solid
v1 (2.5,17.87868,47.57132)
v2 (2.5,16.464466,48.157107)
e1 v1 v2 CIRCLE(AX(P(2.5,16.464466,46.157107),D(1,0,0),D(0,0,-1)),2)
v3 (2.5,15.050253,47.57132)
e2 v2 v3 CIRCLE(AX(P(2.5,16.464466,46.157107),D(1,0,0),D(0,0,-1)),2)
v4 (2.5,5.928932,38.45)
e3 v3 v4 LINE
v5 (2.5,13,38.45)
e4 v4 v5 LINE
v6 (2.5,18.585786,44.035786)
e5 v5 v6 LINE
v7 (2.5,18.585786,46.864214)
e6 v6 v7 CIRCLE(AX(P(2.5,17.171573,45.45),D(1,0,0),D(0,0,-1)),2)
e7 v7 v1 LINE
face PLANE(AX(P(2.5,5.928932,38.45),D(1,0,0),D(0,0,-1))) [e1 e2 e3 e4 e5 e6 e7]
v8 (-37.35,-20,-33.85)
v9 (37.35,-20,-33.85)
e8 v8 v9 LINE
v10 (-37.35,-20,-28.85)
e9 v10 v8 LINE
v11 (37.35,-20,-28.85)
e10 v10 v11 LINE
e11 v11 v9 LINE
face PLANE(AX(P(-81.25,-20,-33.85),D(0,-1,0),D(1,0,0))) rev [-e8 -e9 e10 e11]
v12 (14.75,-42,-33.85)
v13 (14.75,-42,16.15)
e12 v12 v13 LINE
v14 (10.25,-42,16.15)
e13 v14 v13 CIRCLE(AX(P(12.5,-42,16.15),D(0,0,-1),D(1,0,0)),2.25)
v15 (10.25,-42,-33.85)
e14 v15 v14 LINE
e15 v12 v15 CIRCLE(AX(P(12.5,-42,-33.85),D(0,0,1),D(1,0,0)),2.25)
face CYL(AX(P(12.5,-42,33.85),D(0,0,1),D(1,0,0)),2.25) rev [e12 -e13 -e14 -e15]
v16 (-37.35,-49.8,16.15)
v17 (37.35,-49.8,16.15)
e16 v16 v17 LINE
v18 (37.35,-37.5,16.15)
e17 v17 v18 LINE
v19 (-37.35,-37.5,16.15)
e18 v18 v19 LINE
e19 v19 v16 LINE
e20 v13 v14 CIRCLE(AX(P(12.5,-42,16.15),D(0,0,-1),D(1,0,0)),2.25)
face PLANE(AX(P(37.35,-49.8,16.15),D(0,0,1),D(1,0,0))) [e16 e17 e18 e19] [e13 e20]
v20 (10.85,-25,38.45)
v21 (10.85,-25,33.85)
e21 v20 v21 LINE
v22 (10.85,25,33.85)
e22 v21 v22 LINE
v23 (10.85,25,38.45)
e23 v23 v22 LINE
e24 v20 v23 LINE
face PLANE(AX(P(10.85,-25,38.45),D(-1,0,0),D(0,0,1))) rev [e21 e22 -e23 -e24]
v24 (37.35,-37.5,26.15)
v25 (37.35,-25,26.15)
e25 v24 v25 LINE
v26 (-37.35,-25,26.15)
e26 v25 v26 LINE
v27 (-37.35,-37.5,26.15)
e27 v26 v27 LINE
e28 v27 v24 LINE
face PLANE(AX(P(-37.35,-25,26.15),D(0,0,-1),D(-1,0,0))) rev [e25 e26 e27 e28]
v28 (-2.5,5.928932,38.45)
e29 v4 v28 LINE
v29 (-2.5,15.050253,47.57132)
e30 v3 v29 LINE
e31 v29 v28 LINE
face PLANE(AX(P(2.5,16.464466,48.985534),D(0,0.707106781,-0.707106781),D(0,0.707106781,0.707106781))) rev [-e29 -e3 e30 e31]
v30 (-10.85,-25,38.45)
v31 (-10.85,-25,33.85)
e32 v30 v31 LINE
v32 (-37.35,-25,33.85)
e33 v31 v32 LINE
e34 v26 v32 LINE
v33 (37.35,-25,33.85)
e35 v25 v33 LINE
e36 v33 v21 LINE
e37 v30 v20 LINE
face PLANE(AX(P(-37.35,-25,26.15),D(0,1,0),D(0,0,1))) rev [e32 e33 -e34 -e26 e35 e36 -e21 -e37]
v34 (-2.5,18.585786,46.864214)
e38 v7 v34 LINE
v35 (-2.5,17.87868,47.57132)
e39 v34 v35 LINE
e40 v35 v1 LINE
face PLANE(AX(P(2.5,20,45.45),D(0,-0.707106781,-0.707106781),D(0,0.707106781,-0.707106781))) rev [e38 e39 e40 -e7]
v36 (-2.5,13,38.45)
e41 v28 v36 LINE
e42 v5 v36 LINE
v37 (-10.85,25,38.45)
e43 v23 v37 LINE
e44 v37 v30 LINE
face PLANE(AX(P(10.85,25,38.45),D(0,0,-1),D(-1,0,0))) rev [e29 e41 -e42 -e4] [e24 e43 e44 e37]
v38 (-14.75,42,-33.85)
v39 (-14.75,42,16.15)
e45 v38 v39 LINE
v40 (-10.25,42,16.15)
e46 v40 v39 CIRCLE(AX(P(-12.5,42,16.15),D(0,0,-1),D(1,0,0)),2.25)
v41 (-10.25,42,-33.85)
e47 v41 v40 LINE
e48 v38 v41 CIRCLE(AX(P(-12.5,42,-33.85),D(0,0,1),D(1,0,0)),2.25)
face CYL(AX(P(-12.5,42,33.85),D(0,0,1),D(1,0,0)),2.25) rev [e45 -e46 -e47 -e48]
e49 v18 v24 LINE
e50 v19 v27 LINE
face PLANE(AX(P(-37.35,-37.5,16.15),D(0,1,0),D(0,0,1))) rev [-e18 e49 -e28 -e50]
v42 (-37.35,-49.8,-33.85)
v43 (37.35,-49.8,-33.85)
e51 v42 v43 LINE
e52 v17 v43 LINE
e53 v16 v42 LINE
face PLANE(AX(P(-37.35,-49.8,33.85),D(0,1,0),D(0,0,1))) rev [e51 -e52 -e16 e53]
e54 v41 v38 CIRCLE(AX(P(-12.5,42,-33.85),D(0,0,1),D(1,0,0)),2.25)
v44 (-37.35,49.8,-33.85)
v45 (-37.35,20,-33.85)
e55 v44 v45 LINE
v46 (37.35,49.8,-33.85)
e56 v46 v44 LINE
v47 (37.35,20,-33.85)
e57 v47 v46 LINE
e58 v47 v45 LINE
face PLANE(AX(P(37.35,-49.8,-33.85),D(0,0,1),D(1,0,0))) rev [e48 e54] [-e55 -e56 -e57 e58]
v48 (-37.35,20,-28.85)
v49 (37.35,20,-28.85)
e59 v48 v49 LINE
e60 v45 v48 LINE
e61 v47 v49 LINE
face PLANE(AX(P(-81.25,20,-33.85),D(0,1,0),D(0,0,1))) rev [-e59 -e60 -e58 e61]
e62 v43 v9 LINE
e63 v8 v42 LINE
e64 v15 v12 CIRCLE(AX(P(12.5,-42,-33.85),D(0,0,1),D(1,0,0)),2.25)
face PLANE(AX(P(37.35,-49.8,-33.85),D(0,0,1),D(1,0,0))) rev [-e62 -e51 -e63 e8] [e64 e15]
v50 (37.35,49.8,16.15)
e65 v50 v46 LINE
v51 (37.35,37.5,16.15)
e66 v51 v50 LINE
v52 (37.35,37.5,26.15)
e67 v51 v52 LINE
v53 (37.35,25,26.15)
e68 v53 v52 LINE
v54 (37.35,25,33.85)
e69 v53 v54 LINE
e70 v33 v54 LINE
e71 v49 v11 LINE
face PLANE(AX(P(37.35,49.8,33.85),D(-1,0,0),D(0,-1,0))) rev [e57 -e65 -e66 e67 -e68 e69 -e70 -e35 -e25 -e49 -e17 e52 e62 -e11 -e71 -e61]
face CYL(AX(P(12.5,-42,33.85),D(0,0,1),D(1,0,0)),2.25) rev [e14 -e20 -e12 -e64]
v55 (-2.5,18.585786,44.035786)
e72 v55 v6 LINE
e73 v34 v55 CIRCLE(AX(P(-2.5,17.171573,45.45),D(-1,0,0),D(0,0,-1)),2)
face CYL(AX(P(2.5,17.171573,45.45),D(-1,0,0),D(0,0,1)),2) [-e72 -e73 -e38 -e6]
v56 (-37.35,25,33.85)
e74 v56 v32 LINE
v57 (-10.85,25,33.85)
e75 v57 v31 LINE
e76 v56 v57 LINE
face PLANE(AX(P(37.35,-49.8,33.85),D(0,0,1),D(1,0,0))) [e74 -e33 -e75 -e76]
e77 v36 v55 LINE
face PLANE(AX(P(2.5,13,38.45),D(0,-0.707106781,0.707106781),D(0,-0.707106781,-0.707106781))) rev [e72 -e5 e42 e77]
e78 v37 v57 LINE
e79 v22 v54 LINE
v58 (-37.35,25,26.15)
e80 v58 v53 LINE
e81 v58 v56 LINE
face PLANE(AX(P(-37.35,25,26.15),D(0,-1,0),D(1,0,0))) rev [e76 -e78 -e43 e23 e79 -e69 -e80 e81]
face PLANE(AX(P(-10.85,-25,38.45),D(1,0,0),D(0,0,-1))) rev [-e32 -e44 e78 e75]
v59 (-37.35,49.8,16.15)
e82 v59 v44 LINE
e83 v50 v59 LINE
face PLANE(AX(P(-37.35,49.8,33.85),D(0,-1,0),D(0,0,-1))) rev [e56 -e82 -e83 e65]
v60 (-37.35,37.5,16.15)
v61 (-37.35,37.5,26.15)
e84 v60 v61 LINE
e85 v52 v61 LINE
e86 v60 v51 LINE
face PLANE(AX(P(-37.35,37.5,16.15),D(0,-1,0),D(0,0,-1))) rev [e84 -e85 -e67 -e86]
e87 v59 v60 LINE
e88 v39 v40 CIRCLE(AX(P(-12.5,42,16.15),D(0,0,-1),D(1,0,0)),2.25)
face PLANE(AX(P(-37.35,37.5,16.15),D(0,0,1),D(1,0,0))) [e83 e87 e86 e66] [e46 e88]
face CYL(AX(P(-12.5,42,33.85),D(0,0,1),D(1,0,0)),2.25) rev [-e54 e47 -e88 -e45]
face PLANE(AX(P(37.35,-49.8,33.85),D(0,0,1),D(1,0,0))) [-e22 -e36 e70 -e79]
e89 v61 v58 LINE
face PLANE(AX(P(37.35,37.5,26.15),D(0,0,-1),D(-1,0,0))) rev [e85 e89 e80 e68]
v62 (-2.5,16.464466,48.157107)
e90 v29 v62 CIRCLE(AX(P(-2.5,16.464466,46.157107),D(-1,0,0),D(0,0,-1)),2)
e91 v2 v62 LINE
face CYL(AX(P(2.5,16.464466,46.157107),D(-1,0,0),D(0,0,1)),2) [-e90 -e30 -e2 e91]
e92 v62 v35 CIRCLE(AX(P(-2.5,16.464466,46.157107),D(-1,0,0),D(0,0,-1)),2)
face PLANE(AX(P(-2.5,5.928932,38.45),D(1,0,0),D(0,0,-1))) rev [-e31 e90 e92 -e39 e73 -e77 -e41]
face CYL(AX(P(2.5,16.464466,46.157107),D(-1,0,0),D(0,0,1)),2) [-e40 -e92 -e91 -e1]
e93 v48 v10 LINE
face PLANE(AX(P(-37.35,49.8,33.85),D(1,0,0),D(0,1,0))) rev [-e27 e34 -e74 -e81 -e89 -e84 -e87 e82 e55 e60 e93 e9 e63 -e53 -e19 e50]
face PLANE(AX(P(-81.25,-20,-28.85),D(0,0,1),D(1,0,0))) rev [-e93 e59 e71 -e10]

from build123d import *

# Parameters (mm, degrees)
SKETCH1_W                  = 74.7
SKETCH1_H                  = 99.6
BOSS_EXTRUDE1_DEPTH        = 33.85
F_4_5_4_5_DIAMETER_HOLE1_D = 4.5
SKETCH4_W                  = 74.7
SKETCH4_H                  = 12.3
CUT_EXTRUDE1_DEPTH         = 17.7
SKETCH5_W                  = 74.7
SKETCH5_H                  = 12.5
CUT_EXTRUDE2_DEPTH         = 7.7
SKETCH6_W                  = 21.7
SKETCH6_H                  = 50
BOSS_EXTRUDE2_DEPTH        = 4.6
SKETCH7_W                  = 5
SKETCH7_H                  = 40
CUT_EXTRUDE3_DEPTH         = 118.6
BOSS_EXTRUDE3_DEPTH        = 2.5
FILLET1_R                  = 2


with BuildPart() as part:
    # Sketch1 → Boss-Extrude1 (new, symmetric)
    with BuildSketch(Plane.XY):
        Rectangle(SKETCH1_W, SKETCH1_H)
    extrude(amount=BOSS_EXTRUDE1_DEPTH, both=True)

    # Ø4.5 (4.5) Diameter Hole1 (through all)
    with Locations(Plane.XY.offset(33.85)):
        with Locations((-12.5, 42), (12.5, -42)):
            Hole(F_4_5_4_5_DIAMETER_HOLE1_D / 2)

    # Sketch4 → Cut-Extrude1 (cut)
    with BuildSketch(Plane.XY.offset(33.85)):
        with Locations((0, 43.65)):
            Rectangle(SKETCH4_W, SKETCH4_H)
        with Locations((0, -43.65)):
            Rectangle(SKETCH4_W, SKETCH4_H)
    extrude(amount=-CUT_EXTRUDE1_DEPTH, mode=Mode.SUBTRACT)

    # Sketch5 → Cut-Extrude2 (cut)
    with BuildSketch(Plane.XY.offset(33.85)):
        with Locations((0, -31.25)):
            Rectangle(SKETCH5_W, SKETCH5_H)
        with Locations((0, 31.25)):
            Rectangle(SKETCH5_W, SKETCH5_H)
    extrude(amount=-CUT_EXTRUDE2_DEPTH, mode=Mode.SUBTRACT)

    # Sketch6 → Boss-Extrude2 (add)
    with BuildSketch(Plane.XY.offset(33.85)):
        Rectangle(SKETCH6_W, SKETCH6_H)
    extrude(amount=BOSS_EXTRUDE2_DEPTH)

    # Sketch7 → Cut-Extrude3 (cut)
    with BuildSketch(Plane(origin=(37.35, 0, 0), x_dir=(0, 0, -1), z_dir=(1, 0, 0))):
        with Locations((31.35, 0)):
            Rectangle(SKETCH7_W, SKETCH7_H)
    extrude(amount=-CUT_EXTRUDE3_DEPTH, mode=Mode.SUBTRACT)

    # Sketch8 → Boss-Extrude3 (add, symmetric)
    with BuildSketch(Plane(origin=(0, 0, 0), x_dir=(0, 0, -1), z_dir=(1, 0, 0))):
        Polygon((-38.45, 13), (-45.45, 20), (-48.985533906, 16.464466094), (-38.45, 5.928932188), align=None)
    extrude(amount=BOSS_EXTRUDE3_DEPTH, both=True)

    # Fillet1
    fillet1_edges = [part.edges().sort_by_distance(p)[0] for p in [
        (0, 20, 45.45),
        (0, 16.464466094, 48.985533906),
    ]]
    fillet(fillet1_edges, radius=FILLET1_R)


solid = part.part
